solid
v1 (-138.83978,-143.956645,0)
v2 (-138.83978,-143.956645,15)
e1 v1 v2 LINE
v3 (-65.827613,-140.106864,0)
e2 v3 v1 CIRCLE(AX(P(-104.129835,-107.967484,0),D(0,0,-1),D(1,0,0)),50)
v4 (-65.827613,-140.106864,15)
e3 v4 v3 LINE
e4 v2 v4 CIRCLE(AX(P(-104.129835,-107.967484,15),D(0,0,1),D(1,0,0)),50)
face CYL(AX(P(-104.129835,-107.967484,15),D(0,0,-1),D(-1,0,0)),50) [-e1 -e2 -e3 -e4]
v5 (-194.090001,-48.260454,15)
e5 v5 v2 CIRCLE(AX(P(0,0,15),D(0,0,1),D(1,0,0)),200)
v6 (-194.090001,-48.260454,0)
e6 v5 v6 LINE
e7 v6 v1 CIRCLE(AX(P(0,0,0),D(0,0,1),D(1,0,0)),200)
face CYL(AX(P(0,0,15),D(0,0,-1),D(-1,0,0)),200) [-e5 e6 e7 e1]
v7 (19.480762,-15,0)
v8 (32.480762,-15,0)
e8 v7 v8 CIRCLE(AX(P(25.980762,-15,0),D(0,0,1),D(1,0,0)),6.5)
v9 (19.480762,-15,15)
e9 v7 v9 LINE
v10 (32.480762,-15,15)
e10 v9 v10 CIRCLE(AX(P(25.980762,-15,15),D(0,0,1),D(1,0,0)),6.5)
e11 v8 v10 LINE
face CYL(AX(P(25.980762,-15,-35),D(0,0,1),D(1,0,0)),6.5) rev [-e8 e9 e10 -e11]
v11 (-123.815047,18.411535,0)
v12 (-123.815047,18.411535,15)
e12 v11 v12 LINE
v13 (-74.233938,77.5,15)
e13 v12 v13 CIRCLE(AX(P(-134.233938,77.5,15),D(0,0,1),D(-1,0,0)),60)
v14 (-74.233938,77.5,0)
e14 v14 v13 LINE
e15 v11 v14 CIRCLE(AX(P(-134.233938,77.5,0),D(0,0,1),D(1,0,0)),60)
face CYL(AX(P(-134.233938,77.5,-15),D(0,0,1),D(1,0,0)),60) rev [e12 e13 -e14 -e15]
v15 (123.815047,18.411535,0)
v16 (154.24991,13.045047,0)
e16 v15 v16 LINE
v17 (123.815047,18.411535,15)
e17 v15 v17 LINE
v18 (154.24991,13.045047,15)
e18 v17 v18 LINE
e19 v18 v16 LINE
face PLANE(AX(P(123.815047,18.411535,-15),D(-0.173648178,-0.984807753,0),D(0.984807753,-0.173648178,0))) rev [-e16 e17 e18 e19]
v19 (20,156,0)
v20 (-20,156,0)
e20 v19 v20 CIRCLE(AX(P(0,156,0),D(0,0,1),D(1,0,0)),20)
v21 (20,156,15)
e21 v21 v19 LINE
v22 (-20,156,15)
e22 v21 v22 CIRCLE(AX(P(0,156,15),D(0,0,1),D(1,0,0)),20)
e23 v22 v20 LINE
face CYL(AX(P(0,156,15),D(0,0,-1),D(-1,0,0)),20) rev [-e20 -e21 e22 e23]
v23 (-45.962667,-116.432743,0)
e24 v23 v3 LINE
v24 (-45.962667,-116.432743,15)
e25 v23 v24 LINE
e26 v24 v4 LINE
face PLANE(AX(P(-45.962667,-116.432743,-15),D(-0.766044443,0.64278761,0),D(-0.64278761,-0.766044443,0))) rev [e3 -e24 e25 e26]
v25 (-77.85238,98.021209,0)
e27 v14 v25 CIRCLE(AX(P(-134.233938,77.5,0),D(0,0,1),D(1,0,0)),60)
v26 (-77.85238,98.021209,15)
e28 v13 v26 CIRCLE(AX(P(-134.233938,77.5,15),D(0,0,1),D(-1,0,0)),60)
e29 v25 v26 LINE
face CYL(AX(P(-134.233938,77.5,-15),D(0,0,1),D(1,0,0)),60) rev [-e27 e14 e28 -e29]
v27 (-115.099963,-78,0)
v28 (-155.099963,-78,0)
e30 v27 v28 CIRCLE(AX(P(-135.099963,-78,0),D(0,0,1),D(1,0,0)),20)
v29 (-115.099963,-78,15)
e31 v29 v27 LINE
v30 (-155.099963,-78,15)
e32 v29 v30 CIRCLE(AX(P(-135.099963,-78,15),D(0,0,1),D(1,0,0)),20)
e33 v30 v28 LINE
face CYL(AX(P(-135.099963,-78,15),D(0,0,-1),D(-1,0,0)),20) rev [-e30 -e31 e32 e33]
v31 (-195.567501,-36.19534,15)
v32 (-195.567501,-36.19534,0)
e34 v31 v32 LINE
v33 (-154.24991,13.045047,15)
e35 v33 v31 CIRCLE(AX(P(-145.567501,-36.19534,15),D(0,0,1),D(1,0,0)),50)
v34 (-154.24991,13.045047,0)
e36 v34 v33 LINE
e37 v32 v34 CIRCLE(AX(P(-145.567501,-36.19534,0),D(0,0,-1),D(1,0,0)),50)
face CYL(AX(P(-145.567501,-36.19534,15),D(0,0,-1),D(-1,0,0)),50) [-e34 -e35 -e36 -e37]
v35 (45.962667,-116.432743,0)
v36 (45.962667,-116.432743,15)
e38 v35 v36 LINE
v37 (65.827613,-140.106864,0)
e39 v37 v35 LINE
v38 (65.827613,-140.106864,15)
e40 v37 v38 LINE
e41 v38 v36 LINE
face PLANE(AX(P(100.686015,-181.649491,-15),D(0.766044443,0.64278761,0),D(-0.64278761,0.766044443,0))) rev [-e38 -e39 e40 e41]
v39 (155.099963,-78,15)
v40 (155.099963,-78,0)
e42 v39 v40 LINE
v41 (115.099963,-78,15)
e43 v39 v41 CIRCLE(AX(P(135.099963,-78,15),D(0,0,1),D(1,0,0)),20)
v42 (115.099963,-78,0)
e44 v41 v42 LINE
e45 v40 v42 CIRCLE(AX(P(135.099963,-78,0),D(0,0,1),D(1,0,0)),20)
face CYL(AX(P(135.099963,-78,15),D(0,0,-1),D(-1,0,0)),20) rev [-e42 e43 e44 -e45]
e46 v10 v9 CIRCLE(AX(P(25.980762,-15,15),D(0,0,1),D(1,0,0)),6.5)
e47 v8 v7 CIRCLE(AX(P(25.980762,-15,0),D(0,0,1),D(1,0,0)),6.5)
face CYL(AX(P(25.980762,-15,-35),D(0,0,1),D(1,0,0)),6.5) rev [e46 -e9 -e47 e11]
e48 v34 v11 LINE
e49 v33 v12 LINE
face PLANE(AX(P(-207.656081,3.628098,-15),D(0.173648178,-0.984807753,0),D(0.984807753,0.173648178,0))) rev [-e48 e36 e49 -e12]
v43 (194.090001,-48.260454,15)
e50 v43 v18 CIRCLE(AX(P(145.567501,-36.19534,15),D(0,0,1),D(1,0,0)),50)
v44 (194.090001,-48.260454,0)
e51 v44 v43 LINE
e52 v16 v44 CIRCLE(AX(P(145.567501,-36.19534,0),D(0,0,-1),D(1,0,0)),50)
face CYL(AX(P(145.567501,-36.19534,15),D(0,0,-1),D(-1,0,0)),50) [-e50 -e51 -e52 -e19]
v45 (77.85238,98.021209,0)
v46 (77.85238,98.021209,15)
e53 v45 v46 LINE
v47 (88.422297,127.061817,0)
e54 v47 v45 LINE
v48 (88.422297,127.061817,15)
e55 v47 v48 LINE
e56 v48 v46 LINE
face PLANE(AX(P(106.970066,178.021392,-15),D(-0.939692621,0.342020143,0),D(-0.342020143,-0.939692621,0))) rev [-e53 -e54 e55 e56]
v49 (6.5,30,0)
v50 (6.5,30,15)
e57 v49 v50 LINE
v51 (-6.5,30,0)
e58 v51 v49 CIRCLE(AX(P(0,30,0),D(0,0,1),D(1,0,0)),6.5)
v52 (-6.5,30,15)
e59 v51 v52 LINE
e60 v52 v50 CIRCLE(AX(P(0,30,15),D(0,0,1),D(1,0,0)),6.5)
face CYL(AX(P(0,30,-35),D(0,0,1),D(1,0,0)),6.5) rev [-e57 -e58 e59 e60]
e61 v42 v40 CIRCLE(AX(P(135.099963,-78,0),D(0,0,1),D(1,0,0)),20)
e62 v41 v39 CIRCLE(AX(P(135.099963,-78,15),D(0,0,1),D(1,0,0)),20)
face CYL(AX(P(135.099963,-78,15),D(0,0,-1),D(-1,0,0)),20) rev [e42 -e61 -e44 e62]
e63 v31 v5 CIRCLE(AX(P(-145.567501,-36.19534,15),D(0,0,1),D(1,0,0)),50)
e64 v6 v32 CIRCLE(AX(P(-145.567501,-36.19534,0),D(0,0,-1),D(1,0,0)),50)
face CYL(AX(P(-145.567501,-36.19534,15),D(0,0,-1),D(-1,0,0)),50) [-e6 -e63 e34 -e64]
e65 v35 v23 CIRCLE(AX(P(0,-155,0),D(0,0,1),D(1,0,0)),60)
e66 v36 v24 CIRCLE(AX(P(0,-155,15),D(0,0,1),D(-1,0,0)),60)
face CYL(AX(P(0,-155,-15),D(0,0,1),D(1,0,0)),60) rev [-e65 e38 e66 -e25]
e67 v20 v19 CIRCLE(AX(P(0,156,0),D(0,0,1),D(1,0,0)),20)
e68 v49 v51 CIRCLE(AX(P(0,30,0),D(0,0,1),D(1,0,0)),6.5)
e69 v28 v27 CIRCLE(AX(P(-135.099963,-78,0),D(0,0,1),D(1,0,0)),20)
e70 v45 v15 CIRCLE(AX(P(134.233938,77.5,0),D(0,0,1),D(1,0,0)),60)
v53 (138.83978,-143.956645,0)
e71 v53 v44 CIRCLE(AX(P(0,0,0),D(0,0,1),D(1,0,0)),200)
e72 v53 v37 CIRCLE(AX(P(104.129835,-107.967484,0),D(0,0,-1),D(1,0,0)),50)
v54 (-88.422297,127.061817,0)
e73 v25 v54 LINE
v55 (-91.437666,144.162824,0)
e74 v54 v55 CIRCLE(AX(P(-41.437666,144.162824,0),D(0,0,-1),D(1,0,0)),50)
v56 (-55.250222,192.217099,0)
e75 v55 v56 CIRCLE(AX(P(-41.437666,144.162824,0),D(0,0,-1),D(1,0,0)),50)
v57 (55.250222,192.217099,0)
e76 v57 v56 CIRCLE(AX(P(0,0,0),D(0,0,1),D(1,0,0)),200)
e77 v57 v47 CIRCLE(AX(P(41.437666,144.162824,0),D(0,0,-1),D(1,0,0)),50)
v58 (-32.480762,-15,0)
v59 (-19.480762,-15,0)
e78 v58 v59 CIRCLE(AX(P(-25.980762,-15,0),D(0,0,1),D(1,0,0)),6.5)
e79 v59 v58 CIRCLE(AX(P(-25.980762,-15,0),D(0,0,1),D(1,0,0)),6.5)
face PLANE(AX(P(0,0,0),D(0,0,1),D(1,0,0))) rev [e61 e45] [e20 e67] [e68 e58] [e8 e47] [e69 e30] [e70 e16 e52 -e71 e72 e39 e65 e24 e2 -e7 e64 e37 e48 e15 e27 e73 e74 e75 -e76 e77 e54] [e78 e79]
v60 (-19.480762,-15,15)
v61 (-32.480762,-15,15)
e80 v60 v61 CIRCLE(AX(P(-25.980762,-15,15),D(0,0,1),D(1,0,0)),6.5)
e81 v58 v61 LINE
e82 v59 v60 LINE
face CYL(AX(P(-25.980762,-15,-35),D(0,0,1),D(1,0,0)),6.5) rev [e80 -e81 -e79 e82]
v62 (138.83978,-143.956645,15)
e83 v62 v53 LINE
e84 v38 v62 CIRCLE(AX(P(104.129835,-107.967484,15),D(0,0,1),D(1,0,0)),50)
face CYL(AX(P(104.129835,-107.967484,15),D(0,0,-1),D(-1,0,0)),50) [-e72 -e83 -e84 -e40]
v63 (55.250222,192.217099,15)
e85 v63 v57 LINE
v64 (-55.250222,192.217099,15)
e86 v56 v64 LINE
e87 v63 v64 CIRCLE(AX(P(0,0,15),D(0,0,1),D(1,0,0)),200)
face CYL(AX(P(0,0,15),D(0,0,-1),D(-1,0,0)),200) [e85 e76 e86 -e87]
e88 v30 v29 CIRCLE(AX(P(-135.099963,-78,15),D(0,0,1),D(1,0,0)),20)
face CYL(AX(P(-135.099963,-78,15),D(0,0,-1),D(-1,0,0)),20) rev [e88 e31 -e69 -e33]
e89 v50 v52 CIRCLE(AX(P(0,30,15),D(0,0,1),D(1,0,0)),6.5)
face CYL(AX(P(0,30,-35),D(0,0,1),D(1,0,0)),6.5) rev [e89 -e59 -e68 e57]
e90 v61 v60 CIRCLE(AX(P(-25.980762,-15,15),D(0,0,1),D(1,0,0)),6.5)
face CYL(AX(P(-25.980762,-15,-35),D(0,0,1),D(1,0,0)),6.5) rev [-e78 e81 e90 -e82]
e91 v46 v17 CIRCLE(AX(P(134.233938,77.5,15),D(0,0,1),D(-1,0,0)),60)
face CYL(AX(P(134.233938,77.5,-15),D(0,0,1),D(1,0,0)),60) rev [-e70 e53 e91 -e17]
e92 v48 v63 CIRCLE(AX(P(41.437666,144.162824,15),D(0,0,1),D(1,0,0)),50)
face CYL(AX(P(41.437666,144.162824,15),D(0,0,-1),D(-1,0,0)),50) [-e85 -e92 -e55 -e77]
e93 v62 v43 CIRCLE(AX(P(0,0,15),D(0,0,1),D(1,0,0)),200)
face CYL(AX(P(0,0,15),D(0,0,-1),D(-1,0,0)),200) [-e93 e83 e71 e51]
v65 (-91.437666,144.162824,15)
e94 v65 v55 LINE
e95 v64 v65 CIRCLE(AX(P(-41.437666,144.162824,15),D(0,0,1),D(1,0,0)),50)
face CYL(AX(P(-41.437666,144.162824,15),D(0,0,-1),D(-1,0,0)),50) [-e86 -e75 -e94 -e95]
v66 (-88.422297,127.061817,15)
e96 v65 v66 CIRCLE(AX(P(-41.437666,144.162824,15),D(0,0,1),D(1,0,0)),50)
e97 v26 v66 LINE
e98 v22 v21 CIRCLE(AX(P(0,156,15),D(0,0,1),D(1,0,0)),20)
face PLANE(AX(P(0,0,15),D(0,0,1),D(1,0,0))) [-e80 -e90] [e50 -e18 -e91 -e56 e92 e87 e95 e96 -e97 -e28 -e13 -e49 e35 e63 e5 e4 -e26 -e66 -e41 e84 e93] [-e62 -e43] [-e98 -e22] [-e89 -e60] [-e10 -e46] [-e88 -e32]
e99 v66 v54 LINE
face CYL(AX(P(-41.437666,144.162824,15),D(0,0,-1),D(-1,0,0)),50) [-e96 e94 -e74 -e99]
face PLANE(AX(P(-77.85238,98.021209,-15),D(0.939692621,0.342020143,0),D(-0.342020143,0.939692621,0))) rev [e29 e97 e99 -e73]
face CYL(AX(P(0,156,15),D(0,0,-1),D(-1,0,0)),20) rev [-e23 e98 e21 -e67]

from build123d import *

# Parameters (mm, degrees)
SKETCH1_R           = 200
SKETCH1_R_2         = 20
BOSS_EXTRUDE1_DEPTH = 15
CUT_EXTRUDE1_DEPTH  = 30
FILLET1_R           = 50
SKETCH3_R           = 6.5
CUT_EXTRUDE2_DEPTH  = 50


with BuildPart() as part:
    # Sketch1 → Boss-Extrude1 (new body)
    with BuildSketch(Plane.XY):
        Circle(SKETCH1_R)
        with Locations((0, 156)):
            Circle(SKETCH1_R_2, mode=Mode.SUBTRACT)
        with Locations((135.09996299, -78)):
            Circle(SKETCH1_R_2, mode=Mode.SUBTRACT)
        with Locations((-135.09996299, -78)):
            Circle(SKETCH1_R_2, mode=Mode.SUBTRACT)
    extrude(amount=BOSS_EXTRUDE1_DEPTH)

    # Sketch2 → Cut-Extrude1 (cut)
    with BuildSketch(Plane.XY.offset(15)):
        with BuildLine():
            Line((-45.962666587, -116.432743419), (-177.651298468, -273.373143566))
            Line((-177.651298468, -273.373143566), (100.686015144, -181.64949066))
            Line((100.686015144, -181.64949066), (45.962666587, -116.432743419))
            ThreePointArc((45.962666587, -116.432743419), (0, -95), (-45.962666587, -116.432743419))
        make_face()
        with BuildLine():
            Line((-77.852380339, 98.0212086), (-147.922437807, 290.537109271))
            Line((-147.922437807, 290.537109271), (-207.656081069, 3.62809841))
            Line((-207.656081069, 3.62809841), (-123.815046927, 18.411534819))
            ThreePointArc((-123.815046927, 18.411534819), (-82.27241336, 47.5), (-77.852380339, 98.0212086))
        make_face()
        with BuildLine():
            Line((123.815046927, 18.411534819), (325.573736275, -17.163965705))
            Line((325.573736275, -17.163965705), (106.970065924, 178.021392251))
            Line((106.970065924, 178.021392251), (77.852380339, 98.0212086))
            ThreePointArc((77.852380339, 98.0212086), (82.27241336, 47.5), (123.815046927, 18.411534819))
        make_face()
    extrude(amount=-CUT_EXTRUDE1_DEPTH, mode=Mode.SUBTRACT)

    # Fillet1
    fillet1_edges = [part.edges().sort_by_distance(p)[0] for p in [
        (199.937763867, 4.989045978, 7.5),
        (104.289522491, 170.656659696, 7.5),
        (-104.289522491, 170.656659696, 7.5),
        (-199.937763867, 4.989045978, 7.5),
        (-95.648241376, -175.645705674, 7.5),
        (95.648241376, -175.645705674, 7.5),
    ]]
    fillet(fillet1_edges, radius=FILLET1_R)

    # Sketch3 → Cut-Extrude2 (cut)
    with BuildSketch(Plane.XY.offset(15)):
        with Locations((0, 30)):
            Circle(SKETCH3_R)
        with Locations((25.980762114, -15)):
            Circle(SKETCH3_R)
        with Locations((-25.980762114, -15)):
            Circle(SKETCH3_R)
    extrude(amount=-CUT_EXTRUDE2_DEPTH, mode=Mode.SUBTRACT)


solid = part.part
